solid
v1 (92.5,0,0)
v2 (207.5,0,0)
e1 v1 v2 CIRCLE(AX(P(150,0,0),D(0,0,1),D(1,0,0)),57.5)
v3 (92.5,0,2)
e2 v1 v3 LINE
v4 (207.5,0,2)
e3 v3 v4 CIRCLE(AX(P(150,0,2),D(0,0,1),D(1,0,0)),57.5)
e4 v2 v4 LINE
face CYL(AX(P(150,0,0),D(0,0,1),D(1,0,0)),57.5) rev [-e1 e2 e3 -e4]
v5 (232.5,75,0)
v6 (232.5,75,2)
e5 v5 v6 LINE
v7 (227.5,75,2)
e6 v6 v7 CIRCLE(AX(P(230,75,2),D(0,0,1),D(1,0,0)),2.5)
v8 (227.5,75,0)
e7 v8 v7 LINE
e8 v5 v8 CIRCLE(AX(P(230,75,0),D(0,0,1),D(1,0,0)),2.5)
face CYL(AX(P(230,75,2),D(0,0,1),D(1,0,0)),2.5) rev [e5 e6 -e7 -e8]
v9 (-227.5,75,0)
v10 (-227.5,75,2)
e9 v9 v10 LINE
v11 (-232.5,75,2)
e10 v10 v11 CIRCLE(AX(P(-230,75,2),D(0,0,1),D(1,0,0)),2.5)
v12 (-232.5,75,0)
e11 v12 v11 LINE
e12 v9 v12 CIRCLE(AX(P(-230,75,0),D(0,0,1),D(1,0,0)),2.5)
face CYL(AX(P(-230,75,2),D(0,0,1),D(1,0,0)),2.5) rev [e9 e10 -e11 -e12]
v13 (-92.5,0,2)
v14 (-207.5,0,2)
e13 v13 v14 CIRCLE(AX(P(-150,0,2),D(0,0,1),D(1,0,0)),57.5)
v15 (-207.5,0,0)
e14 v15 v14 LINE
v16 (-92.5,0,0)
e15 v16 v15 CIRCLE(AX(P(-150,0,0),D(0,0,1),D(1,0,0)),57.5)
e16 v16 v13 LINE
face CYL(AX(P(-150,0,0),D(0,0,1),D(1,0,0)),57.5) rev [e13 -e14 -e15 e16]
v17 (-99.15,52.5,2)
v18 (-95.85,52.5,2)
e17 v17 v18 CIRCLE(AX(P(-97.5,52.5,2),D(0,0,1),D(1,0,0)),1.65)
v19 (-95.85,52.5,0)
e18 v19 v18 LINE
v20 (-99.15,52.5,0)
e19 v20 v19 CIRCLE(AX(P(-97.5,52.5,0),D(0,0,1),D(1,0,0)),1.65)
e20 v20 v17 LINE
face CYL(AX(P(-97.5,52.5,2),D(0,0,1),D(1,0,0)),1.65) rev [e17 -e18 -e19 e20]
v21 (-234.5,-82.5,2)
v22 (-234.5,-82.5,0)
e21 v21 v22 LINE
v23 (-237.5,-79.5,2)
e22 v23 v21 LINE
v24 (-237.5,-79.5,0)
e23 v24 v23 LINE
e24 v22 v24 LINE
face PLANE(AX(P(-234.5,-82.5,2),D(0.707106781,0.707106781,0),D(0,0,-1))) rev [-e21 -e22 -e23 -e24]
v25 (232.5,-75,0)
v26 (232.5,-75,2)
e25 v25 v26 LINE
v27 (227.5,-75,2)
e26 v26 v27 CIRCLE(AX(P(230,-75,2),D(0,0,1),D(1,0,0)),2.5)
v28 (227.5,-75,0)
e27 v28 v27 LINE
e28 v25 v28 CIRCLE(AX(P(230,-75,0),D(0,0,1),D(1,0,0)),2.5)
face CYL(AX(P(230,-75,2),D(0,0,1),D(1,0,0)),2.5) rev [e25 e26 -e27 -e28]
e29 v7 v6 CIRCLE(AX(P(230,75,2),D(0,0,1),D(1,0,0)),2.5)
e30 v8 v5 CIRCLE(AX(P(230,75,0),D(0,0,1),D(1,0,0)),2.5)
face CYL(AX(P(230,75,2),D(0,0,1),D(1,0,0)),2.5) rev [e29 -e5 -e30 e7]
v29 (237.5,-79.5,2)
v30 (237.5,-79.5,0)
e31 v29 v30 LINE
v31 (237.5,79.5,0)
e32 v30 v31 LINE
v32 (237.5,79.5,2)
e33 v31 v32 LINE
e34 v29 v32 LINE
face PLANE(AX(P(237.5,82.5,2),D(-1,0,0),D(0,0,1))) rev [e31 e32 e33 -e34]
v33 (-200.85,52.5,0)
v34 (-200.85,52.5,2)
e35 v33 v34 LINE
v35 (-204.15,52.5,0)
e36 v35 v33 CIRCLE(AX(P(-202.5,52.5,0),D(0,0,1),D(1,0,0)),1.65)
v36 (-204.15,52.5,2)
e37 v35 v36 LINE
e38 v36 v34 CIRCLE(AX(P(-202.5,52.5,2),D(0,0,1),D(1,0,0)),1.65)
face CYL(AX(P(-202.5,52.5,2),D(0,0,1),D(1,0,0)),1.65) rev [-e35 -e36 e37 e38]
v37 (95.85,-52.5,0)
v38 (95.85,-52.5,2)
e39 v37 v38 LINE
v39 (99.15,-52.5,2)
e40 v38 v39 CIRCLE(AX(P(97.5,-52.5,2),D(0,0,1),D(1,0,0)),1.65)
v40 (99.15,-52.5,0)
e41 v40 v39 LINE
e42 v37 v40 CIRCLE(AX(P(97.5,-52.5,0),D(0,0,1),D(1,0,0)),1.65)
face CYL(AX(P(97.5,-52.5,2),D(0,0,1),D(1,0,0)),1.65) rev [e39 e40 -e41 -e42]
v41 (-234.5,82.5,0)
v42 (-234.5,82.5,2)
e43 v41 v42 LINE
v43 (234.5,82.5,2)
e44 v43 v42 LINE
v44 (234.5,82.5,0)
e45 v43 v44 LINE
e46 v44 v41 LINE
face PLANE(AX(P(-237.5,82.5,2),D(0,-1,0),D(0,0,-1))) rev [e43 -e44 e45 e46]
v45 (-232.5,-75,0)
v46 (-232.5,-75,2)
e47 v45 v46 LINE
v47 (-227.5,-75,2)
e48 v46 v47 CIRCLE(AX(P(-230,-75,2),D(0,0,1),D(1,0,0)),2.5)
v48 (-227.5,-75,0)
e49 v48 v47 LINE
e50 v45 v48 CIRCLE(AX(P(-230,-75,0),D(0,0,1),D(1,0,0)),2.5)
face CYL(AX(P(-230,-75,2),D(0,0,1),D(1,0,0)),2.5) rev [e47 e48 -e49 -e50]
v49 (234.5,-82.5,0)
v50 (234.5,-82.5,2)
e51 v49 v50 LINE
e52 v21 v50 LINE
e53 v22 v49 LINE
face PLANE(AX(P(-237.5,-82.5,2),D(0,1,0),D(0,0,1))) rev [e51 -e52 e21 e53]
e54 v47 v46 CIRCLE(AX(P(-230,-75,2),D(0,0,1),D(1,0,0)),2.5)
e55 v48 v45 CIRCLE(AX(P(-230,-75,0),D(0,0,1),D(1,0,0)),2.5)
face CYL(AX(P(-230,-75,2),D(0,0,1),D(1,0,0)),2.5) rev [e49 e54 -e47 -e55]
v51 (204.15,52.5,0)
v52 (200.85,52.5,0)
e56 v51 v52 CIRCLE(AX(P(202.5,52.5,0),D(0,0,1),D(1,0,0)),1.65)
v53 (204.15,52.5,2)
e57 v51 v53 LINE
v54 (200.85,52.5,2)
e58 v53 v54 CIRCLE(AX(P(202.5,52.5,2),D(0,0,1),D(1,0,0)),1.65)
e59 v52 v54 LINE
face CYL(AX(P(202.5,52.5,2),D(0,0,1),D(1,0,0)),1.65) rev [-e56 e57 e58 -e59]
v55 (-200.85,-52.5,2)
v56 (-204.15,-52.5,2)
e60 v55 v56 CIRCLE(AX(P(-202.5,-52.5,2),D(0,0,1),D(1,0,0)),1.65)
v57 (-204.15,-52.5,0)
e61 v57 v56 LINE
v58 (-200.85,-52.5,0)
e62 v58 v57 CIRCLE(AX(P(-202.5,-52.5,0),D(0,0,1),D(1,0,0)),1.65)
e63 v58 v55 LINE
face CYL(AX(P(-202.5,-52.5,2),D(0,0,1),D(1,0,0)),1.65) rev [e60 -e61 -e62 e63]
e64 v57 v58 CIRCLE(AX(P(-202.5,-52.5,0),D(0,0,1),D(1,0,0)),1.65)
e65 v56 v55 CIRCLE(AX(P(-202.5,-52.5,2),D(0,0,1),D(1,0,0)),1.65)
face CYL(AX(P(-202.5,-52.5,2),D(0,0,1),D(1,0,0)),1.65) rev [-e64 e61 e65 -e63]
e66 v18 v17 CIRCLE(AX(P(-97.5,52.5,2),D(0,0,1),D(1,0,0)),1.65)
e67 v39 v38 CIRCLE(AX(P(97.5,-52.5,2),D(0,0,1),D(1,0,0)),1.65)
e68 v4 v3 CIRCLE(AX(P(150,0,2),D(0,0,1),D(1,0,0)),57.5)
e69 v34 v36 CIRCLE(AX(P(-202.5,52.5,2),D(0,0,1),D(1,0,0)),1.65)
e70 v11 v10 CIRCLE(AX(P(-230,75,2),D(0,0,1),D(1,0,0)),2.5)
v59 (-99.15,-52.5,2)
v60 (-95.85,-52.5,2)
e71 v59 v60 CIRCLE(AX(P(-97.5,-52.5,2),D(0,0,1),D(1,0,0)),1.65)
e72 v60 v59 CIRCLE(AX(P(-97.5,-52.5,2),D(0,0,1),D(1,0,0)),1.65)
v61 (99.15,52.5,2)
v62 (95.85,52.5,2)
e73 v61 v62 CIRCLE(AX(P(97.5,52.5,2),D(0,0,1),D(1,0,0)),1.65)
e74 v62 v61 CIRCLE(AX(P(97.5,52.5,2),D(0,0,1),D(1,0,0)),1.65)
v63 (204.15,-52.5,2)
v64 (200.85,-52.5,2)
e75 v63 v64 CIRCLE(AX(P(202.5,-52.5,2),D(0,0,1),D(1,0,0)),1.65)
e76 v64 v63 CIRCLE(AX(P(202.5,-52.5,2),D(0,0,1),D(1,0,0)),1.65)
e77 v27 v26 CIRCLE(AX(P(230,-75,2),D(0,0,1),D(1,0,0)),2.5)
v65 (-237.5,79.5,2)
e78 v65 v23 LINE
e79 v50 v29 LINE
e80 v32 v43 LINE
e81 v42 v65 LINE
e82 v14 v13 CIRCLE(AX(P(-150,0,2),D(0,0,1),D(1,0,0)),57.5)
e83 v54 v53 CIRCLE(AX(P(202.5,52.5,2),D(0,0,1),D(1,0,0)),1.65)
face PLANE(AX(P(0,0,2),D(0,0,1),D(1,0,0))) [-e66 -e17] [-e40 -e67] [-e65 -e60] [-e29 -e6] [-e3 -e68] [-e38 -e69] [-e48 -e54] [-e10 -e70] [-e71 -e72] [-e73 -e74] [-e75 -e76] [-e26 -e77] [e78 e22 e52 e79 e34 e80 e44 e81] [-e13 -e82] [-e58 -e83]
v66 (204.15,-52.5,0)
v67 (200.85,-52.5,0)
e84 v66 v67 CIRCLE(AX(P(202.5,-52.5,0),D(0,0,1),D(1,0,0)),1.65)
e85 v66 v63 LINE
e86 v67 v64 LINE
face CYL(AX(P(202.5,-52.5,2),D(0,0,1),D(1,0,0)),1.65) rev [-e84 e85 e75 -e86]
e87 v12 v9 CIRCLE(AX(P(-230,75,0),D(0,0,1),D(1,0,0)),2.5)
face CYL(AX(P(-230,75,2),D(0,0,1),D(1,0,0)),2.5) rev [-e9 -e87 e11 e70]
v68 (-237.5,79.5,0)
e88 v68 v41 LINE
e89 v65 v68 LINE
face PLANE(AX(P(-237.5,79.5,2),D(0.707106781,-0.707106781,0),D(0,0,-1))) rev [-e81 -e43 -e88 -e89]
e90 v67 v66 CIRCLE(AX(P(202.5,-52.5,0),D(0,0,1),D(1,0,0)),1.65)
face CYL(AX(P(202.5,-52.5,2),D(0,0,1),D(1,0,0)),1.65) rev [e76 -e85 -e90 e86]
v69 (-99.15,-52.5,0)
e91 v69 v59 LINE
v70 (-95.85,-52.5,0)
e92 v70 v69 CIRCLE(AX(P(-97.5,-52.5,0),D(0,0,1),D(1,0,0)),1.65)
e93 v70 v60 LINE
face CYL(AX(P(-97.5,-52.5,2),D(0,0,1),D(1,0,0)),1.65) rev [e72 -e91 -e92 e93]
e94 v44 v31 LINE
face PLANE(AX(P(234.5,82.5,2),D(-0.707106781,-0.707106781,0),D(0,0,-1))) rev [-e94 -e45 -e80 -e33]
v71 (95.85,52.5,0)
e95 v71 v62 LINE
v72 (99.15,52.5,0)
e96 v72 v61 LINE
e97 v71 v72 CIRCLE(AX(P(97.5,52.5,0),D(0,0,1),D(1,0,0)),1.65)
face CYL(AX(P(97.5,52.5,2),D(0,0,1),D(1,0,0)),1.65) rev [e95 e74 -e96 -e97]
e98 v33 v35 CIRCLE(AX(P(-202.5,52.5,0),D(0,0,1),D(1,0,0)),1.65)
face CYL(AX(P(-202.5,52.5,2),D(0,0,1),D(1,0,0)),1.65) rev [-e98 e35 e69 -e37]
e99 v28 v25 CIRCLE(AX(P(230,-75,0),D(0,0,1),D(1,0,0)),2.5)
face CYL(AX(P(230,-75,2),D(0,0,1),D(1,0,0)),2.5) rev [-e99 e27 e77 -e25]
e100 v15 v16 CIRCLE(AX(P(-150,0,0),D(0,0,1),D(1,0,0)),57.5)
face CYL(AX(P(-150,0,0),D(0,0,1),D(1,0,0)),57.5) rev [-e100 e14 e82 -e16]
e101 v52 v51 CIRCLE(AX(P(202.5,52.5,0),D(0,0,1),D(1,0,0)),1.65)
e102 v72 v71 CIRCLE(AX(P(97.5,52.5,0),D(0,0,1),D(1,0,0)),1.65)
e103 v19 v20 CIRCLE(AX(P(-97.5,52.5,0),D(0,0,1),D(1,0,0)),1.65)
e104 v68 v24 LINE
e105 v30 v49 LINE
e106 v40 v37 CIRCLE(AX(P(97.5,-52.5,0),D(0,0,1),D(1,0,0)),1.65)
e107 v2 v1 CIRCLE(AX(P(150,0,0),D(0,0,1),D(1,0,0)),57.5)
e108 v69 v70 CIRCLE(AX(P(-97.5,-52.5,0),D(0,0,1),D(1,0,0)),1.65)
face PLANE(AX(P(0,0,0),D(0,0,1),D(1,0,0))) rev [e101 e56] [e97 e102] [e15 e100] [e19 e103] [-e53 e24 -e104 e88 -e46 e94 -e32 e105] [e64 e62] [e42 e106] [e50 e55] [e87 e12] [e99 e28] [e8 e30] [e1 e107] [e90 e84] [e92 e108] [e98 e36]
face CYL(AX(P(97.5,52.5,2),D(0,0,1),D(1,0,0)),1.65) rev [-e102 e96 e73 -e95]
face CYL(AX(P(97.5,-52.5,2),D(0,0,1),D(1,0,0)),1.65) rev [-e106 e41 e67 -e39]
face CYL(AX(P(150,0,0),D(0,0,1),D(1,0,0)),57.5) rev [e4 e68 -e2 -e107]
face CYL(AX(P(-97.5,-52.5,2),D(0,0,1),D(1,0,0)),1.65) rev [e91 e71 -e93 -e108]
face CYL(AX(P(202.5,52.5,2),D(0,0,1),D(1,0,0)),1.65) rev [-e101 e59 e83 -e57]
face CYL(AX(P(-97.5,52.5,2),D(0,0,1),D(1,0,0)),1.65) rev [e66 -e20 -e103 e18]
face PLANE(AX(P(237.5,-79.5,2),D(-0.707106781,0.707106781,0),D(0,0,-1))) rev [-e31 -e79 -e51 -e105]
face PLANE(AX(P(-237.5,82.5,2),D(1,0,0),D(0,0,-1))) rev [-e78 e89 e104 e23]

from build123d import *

# Parameters (mm, degrees)
SKETCH_1_W             = 475
SKETCH_1_H             = 165
EXTRUDE_1_DEPTH        = 2
HOLE_WIZARD_5_0_5_1_D  = 5
CHAMFER_1_SIZE         = 3
SKETCH_4_R             = 57.5
CUT_EXTRUDE_1_DEPTH    = 2
HOLE_WIZARD_M4_1_D     = 3.3
HOLE_WIZARD_M4_1_DEPTH = 10.1
HOLE_WIZARD_M4_1_TIP   = 0.991420021


with BuildPart() as part:
    # 草图1 → 凸台-拉伸1 (new body)
    with BuildSketch(Plane.XY):
        Rectangle(SKETCH_1_W, SKETCH_1_H)
    extrude(amount=EXTRUDE_1_DEPTH)

    # Ø5.0 (5) 直径孔1 (through all)
    with Locations(Plane.XY.offset(2)):
        with Locations((-230, 75), (-230, -75), (230, 75), (230, -75)):
            Hole(HOLE_WIZARD_5_0_5_1_D / 2)

    # 倒角1
    chamfer_1_edges = [part.edges().sort_by_distance(p)[0] for p in [
        (237.5, -82.5, 1),
        (-237.5, -82.5, 1),
        (-237.5, 82.5, 1),
        (237.5, 82.5, 1),
    ]]
    chamfer(chamfer_1_edges, length=CHAMFER_1_SIZE)

    # 草图4 → 切除-拉伸1 (cut)
    with BuildSketch(Plane.XY.offset(2)):
        with Locations((-150, 0)):
            Circle(SKETCH_4_R)
        with Locations((150, 0)):
            Circle(SKETCH_4_R)
    extrude(amount=-CUT_EXTRUDE_1_DEPTH, mode=Mode.SUBTRACT)

    # M4 螺纹孔1
    with Locations(Plane.XY.offset(2)):
        with Locations((-202.5, 52.5), (-97.5, 52.5), (-97.5, -52.5), (-202.5, -52.5), (97.5, -52.5), (202.5, -52.5), (202.5, 52.5), (97.5, 52.5)):
            Hole(HOLE_WIZARD_M4_1_D / 2, depth=HOLE_WIZARD_M4_1_DEPTH)
            with Locations((0, 0, -(HOLE_WIZARD_M4_1_DEPTH + HOLE_WIZARD_M4_1_TIP / 2))):  # 118° drill point
                Cone(0, HOLE_WIZARD_M4_1_D / 2, HOLE_WIZARD_M4_1_TIP, mode=Mode.SUBTRACT)


solid = part.part
